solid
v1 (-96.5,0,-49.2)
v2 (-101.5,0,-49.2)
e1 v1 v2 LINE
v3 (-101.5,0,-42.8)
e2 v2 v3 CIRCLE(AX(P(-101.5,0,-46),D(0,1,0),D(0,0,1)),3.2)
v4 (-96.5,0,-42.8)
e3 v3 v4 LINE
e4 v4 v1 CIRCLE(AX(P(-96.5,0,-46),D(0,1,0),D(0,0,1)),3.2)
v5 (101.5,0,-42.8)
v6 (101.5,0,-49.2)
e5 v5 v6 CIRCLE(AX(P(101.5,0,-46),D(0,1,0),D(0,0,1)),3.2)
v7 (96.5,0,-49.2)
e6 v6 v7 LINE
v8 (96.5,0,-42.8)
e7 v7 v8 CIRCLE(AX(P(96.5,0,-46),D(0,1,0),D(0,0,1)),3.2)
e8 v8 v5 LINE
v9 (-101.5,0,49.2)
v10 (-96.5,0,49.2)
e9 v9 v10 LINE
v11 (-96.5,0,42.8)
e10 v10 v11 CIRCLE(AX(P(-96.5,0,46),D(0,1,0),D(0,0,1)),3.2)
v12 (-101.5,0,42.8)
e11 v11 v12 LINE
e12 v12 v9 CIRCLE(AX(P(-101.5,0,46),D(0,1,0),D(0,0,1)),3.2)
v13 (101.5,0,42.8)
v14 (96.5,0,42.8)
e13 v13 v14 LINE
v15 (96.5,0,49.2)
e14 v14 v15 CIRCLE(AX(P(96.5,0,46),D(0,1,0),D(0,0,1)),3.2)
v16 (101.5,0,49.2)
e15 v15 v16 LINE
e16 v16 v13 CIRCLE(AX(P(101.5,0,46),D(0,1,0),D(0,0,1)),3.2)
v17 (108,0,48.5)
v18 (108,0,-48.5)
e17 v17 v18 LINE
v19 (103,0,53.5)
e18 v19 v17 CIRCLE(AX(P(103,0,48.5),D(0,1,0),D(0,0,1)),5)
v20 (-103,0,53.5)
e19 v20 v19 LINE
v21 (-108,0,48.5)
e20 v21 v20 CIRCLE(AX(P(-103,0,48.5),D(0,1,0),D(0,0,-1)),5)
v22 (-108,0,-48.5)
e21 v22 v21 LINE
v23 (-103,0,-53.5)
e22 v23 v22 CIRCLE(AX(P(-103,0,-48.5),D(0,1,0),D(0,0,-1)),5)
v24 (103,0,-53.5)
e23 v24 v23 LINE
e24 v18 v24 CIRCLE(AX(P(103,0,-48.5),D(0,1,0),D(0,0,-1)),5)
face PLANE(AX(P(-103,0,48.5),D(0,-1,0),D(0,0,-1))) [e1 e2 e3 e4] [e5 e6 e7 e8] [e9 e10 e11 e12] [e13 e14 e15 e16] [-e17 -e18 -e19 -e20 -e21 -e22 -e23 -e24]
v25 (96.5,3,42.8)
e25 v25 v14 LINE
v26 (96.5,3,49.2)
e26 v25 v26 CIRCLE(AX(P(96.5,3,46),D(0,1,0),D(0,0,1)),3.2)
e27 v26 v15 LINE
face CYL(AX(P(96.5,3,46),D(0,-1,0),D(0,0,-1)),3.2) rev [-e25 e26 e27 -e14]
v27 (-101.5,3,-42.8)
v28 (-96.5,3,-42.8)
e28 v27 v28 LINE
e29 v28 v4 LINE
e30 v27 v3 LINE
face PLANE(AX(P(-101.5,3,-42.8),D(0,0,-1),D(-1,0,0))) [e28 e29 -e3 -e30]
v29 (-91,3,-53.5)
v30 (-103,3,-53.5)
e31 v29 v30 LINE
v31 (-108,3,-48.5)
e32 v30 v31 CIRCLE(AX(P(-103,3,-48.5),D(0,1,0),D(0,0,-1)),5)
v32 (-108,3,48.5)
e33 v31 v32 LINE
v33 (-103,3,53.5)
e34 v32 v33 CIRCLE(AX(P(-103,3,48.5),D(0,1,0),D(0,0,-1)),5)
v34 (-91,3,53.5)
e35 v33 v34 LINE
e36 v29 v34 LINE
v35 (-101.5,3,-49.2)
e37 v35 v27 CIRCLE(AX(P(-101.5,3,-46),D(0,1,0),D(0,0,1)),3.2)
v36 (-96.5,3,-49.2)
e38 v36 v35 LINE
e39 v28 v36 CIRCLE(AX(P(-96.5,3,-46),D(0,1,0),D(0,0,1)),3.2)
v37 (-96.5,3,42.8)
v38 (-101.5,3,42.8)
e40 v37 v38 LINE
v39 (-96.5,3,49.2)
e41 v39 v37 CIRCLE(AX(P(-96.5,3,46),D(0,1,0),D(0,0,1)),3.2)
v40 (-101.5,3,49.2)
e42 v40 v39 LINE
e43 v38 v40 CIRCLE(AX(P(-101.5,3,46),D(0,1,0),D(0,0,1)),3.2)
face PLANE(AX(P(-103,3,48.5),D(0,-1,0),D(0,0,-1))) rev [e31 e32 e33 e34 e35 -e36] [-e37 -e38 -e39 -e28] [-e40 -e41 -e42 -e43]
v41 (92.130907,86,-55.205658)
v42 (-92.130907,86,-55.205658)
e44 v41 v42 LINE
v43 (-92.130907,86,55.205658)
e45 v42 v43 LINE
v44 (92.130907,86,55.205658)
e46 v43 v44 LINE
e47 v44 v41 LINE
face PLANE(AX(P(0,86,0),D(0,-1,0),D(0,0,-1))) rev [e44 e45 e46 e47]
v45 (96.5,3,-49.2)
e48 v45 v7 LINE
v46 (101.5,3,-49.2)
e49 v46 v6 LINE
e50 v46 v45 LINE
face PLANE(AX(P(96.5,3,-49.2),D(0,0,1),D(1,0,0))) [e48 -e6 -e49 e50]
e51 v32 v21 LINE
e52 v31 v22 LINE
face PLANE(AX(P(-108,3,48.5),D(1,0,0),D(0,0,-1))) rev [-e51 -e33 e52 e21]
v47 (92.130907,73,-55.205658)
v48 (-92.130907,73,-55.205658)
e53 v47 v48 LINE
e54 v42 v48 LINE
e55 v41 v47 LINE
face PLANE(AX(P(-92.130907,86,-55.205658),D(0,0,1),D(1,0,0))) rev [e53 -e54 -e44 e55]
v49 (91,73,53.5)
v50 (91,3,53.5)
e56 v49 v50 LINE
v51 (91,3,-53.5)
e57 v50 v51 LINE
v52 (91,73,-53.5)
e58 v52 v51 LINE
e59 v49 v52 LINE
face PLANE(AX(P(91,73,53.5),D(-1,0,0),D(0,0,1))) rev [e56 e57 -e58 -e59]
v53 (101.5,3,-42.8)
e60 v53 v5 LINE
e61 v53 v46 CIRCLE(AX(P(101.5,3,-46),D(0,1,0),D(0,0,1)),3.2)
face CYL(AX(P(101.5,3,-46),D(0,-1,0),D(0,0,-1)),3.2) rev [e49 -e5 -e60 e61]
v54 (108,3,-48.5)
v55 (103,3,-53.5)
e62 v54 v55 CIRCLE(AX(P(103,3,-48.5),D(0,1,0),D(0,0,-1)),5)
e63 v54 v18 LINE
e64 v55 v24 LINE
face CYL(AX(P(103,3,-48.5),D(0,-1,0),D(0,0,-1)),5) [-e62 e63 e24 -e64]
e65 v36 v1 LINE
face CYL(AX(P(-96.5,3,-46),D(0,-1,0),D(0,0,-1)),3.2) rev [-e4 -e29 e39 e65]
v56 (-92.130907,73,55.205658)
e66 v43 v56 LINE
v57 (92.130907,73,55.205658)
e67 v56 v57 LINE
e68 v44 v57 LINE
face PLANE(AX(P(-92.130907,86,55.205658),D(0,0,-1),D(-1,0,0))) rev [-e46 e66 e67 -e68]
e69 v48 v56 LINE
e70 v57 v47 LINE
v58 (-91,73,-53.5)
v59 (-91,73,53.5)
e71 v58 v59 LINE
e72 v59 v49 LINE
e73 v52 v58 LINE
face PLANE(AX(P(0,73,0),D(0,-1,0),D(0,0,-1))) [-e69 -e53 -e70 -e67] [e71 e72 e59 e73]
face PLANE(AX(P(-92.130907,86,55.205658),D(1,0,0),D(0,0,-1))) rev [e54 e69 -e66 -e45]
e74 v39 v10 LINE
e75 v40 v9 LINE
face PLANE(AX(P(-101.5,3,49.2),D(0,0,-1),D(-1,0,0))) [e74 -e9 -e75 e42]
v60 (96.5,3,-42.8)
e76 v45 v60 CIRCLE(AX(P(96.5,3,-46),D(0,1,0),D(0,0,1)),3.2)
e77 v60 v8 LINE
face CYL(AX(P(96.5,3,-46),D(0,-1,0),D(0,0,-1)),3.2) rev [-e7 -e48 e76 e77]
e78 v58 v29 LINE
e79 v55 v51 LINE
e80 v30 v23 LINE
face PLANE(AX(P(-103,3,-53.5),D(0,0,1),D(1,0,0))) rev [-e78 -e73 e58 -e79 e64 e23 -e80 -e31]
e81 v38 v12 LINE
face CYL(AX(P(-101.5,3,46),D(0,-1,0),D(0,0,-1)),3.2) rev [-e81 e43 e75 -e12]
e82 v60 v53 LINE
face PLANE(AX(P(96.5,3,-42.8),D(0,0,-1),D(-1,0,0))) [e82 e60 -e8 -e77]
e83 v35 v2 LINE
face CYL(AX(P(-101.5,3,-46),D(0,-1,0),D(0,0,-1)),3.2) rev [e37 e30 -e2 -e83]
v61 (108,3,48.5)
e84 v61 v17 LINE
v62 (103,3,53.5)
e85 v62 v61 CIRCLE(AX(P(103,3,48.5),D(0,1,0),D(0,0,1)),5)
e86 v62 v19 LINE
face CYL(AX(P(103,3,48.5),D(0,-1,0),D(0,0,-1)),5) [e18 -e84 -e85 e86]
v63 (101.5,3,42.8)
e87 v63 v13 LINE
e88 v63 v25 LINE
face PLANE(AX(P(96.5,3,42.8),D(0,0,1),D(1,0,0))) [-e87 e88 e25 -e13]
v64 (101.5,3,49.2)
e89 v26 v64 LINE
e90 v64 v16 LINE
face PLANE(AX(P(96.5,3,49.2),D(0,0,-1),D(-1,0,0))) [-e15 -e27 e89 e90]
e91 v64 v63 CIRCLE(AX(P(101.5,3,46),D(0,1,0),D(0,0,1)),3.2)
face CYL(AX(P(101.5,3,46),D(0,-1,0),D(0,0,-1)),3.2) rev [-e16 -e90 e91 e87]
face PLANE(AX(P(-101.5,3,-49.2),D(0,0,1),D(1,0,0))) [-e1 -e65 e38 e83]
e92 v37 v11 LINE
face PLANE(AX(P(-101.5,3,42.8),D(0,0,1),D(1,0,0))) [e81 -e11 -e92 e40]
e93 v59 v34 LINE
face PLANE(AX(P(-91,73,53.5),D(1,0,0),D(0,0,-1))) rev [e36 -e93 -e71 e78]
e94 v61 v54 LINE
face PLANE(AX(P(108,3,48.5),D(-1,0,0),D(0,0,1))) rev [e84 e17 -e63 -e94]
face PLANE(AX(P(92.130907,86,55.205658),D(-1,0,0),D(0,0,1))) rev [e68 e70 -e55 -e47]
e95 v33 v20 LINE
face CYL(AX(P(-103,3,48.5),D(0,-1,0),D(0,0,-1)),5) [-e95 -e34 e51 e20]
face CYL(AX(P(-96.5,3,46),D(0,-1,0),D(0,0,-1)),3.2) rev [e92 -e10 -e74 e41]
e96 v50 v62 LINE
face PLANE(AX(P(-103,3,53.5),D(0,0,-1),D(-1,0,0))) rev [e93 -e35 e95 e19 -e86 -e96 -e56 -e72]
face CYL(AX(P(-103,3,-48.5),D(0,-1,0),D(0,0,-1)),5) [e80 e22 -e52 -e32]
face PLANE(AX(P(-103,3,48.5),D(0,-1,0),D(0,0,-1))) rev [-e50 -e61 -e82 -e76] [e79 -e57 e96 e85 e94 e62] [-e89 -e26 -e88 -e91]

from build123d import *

# Parameters (mm, degrees)
BOSS_EXTRUDE1_DEPTH = 3
SKETCH2_W           = 182
SKETCH2_H           = 107
BOSS_EXTRUDE2_DEPTH = 70
SKETCH4_W           = 184.261814912
SKETCH4_H           = 110.411316032
BOSS_EXTRUDE3_DEPTH = 13


with BuildPart() as part:
    # Sketch1 → Boss-Extrude1 (new body)
    with BuildSketch(Plane(origin=(0, 0, 0), x_dir=(1, 0, 0), z_dir=(0, 1, 0))):
        with BuildLine():
            Line((-103, -53.5), (103, -53.5))
            ThreePointArc((103, -53.5), (106.535533906, -52.035533906), (108, -48.5))
            Line((108, -48.5), (108, 48.5))
            ThreePointArc((108, 48.5), (106.535533906, 52.035533906), (103, 53.5))
            Line((103, 53.5), (-103, 53.5))
            ThreePointArc((-103, 53.5), (-106.535533906, 52.035533906), (-108, 48.5))
            Line((-108, 48.5), (-108, -48.5))
            ThreePointArc((-108, -48.5), (-106.535533906, -52.035533906), (-103, -53.5))
        make_face()
        with BuildLine():
            Line((-101.5, 49.2), (-96.5, 49.2))
            ThreePointArc((-96.5, 49.2), (-93.3, 46), (-96.5, 42.8))
            Line((-96.5, 42.8), (-101.5, 42.8))
            ThreePointArc((-101.5, 42.8), (-104.7, 46), (-101.5, 49.2))
        make_face(mode=Mode.SUBTRACT)
        with BuildLine():
            Line((96.5, 49.2), (101.5, 49.2))
            ThreePointArc((101.5, 49.2), (104.7, 46), (101.5, 42.8))
            Line((101.5, 42.8), (96.5, 42.8))
            ThreePointArc((96.5, 42.8), (93.3, 46), (96.5, 49.2))
        make_face(mode=Mode.SUBTRACT)
        with BuildLine():
            Line((-101.5, -42.8), (-96.5, -42.8))
            ThreePointArc((-96.5, -42.8), (-93.3, -46), (-96.5, -49.2))
            Line((-96.5, -49.2), (-101.5, -49.2))
            ThreePointArc((-101.5, -49.2), (-104.7, -46), (-101.5, -42.8))
        make_face(mode=Mode.SUBTRACT)
        with BuildLine():
            Line((96.5, -42.8), (101.5, -42.8))
            ThreePointArc((101.5, -42.8), (104.7, -46), (101.5, -49.2))
            Line((101.5, -49.2), (96.5, -49.2))
            ThreePointArc((96.5, -49.2), (93.3, -46), (96.5, -42.8))
        make_face(mode=Mode.SUBTRACT)
    extrude(amount=BOSS_EXTRUDE1_DEPTH)

    # Sketch2 → Boss-Extrude2 (add)
    with BuildSketch(Plane(origin=(0, 3, 0), x_dir=(1, 0, 0), z_dir=(0, 1, 0))):
        Rectangle(SKETCH2_W, SKETCH2_H)
    extrude(amount=BOSS_EXTRUDE2_DEPTH)

    # Sketch4 → Boss-Extrude3 (add)
    with BuildSketch(Plane(origin=(0, 73, 0), x_dir=(1, 0, 0), z_dir=(0, 1, 0))):
        Rectangle(SKETCH4_W, SKETCH4_H)
    extrude(amount=BOSS_EXTRUDE3_DEPTH)


solid = part.part
